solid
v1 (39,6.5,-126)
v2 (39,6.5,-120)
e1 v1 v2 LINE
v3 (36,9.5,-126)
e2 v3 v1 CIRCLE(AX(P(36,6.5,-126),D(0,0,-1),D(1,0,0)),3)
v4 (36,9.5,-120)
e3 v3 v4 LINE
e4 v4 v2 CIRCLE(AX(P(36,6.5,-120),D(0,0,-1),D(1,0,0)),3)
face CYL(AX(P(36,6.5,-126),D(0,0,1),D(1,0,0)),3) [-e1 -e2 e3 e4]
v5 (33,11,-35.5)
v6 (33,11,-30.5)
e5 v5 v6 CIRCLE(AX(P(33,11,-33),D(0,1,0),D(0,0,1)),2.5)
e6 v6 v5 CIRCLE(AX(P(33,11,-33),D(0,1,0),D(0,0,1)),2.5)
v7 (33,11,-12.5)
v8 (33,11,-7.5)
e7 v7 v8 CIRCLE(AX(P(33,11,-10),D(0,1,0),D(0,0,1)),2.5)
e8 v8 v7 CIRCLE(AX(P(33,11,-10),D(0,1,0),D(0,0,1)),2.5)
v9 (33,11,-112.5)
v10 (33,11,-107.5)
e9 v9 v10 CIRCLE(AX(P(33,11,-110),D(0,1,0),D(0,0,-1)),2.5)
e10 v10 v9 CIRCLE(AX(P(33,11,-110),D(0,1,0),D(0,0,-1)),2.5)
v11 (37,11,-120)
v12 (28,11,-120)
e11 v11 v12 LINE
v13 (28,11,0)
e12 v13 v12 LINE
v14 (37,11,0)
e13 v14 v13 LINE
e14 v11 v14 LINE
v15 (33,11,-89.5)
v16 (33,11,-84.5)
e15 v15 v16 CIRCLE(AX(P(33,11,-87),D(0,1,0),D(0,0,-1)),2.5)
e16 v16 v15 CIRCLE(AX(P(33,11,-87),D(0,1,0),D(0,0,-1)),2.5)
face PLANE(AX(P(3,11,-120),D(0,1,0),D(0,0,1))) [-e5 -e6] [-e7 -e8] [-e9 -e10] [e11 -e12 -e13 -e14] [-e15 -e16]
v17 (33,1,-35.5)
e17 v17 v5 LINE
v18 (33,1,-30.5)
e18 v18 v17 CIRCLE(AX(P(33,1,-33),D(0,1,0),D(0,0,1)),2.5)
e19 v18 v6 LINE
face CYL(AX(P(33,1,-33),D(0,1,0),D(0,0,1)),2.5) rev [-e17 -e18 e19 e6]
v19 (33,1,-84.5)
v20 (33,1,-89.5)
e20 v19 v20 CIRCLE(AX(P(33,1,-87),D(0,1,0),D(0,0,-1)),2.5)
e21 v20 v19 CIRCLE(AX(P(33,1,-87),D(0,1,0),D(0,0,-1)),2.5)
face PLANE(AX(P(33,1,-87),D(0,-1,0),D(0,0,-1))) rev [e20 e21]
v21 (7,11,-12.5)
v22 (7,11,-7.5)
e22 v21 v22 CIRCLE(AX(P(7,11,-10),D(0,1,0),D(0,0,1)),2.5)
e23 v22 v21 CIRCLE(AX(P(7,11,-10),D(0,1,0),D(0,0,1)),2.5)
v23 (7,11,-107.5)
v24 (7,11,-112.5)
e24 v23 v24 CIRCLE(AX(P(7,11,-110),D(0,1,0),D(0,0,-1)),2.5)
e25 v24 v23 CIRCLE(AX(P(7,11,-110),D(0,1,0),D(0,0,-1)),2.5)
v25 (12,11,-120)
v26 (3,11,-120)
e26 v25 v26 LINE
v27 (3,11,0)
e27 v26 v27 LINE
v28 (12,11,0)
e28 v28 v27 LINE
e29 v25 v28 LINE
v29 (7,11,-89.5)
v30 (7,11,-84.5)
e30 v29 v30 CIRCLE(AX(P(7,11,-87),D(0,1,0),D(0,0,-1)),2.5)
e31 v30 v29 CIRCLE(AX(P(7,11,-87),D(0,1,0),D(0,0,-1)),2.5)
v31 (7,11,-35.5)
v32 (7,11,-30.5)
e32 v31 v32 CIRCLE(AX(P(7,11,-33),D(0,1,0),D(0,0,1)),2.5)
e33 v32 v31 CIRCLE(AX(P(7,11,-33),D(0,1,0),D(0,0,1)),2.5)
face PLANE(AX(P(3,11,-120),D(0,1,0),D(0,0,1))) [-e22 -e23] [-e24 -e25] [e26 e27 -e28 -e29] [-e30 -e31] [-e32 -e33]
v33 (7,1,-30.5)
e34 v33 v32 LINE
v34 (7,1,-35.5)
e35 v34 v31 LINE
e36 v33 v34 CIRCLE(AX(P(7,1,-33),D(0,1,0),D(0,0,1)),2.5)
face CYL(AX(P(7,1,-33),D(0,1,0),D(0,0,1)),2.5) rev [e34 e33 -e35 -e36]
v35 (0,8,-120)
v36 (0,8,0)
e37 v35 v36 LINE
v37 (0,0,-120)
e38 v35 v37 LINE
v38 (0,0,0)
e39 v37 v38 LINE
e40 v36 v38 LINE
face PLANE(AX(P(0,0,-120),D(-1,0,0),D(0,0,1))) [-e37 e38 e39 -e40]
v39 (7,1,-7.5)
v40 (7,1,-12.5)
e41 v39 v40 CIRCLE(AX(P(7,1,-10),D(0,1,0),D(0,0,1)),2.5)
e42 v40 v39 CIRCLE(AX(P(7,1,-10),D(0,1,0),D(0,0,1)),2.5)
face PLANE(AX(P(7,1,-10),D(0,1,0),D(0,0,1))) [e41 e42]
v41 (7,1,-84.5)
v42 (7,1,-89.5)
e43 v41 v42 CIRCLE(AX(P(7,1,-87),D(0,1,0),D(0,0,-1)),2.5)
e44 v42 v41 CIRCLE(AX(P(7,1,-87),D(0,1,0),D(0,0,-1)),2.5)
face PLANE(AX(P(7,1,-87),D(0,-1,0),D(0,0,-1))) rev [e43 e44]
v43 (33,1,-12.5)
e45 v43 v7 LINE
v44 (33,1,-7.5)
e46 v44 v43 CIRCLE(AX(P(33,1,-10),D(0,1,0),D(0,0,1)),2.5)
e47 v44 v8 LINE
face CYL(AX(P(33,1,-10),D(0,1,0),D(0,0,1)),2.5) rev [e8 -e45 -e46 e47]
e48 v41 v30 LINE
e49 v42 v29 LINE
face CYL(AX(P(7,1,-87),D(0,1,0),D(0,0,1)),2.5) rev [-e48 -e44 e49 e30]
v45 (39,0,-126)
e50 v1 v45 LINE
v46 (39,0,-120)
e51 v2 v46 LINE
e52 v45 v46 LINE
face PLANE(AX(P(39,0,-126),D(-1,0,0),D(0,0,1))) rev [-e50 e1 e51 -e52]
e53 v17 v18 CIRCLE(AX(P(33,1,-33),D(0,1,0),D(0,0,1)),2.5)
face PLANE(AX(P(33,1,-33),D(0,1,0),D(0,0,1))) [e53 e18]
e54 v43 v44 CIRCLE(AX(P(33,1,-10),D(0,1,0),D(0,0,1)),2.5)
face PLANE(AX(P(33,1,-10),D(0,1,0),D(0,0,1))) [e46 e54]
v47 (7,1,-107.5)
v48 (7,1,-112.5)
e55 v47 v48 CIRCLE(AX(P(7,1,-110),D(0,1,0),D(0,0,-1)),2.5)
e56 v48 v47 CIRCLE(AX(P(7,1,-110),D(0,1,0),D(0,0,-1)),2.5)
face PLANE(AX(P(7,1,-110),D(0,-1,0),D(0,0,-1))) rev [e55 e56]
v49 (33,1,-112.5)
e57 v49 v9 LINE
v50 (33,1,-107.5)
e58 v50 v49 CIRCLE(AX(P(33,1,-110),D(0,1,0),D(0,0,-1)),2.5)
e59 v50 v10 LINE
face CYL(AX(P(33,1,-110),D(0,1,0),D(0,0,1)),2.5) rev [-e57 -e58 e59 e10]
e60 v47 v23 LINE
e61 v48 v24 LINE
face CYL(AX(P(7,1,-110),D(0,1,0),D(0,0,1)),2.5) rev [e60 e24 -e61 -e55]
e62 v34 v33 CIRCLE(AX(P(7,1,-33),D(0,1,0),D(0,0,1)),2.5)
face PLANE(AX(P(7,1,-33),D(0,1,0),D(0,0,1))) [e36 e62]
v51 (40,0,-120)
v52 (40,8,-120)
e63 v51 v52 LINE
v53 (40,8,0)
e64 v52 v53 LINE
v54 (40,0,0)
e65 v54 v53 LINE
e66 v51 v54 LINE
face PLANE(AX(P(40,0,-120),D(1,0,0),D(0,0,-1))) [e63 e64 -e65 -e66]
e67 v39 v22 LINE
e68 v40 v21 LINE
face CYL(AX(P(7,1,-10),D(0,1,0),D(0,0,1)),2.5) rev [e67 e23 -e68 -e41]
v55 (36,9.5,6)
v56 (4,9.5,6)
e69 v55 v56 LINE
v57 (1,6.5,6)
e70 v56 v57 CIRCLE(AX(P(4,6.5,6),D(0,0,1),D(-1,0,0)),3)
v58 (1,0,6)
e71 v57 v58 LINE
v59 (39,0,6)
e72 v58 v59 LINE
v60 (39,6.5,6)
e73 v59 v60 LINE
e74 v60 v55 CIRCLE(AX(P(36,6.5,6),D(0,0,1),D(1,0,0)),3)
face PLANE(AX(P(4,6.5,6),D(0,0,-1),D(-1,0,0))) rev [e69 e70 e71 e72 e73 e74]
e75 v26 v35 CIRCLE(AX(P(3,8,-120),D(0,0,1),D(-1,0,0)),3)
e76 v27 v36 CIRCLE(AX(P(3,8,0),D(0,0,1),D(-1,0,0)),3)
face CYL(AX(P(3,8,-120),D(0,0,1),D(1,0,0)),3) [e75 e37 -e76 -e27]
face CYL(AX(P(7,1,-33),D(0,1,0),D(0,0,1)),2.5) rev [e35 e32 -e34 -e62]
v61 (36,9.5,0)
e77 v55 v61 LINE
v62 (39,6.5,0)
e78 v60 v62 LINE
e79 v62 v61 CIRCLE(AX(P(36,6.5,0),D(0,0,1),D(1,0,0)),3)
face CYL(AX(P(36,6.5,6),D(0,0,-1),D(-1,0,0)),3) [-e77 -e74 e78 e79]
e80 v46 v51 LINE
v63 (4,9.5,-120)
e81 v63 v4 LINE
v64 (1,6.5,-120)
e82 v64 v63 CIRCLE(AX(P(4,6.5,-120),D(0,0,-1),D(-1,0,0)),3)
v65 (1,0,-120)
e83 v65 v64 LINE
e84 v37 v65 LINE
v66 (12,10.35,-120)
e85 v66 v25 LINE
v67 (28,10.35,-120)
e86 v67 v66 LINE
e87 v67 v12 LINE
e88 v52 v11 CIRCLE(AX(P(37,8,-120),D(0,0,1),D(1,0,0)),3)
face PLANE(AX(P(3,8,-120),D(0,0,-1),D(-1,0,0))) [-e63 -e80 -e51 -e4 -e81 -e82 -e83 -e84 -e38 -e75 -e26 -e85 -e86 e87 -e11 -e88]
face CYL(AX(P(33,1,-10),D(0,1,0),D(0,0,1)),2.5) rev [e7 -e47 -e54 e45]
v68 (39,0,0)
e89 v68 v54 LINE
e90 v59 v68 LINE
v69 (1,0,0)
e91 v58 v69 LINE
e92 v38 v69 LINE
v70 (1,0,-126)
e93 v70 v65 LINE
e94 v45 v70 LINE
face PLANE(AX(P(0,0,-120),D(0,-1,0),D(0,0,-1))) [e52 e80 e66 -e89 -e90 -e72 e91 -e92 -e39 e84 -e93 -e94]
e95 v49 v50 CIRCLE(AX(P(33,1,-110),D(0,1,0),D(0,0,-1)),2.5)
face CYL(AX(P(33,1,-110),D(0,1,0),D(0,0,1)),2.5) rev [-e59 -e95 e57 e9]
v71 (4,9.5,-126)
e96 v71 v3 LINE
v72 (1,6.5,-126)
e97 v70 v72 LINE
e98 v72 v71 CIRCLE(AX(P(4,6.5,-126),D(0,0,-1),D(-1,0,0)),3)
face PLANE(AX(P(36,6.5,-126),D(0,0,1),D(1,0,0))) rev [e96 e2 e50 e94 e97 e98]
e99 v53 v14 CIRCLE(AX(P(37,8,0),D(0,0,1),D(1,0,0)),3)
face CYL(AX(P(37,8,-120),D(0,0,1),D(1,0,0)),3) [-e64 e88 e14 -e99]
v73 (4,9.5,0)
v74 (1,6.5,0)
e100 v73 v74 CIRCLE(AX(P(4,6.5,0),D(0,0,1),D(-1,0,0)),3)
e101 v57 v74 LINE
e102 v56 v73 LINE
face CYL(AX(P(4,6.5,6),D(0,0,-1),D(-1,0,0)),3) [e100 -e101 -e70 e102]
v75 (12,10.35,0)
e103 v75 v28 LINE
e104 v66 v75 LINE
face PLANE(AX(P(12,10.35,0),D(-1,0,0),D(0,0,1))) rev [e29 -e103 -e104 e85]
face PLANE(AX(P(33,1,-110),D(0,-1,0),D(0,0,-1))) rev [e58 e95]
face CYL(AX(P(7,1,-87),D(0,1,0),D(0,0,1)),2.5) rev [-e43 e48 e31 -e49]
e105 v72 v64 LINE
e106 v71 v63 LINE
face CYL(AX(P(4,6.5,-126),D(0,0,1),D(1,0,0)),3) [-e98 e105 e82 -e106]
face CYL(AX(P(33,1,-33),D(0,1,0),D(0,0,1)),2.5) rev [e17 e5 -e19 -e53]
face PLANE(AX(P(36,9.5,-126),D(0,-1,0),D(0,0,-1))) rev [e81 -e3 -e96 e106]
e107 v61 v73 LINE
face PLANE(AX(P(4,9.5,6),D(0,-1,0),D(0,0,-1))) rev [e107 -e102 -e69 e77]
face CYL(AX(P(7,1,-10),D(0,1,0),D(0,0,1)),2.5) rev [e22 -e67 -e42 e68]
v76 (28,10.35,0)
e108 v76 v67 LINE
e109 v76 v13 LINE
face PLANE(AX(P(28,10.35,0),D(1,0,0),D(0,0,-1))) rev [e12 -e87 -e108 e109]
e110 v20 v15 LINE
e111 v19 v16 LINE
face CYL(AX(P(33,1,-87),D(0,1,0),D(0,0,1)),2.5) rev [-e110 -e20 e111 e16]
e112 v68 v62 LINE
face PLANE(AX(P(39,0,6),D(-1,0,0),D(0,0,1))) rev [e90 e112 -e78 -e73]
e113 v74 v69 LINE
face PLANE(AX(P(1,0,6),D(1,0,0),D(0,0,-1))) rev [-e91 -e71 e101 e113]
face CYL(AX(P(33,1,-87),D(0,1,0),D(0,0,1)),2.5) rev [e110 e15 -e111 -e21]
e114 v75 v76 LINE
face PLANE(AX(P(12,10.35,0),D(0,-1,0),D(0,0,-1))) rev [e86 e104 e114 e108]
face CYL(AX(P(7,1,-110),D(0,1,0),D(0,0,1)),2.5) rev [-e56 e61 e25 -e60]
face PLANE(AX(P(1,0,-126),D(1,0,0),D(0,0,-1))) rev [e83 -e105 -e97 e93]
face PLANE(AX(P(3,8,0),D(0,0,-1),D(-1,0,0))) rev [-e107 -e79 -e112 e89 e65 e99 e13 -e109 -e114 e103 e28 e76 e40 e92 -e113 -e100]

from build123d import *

# Parameters (mm, degrees)
EXTRUDE_263_DEPTH   = 120
EXTRUDE_1_DEPTH     = 6
EXTRUDE_START       = 6
EXTRUDE_2_DEPTH     = 6
SKETCH_4_R          = 2.5
CUT_EXTRUDE_1_DEPTH = 10
SKETCH_5_W          = 16
SKETCH_5_H          = 120
CUT_EXTRUDE_2_DEPTH = 0.65


with BuildPart() as part:
    # 草图1 → Extrude 263 (new body)
    with BuildSketch(Plane.XY):
        with BuildLine():
            Line((0, 0), (40, 0))
            Line((40, 0), (40, 8))
            ThreePointArc((40, 8), (39.121320344, 10.121320344), (37, 11))
            Line((37, 11), (3, 11))
            ThreePointArc((3, 11), (0.878679656, 10.121320344), (0, 8))
            Line((0, 8), (0, 0))
        make_face()
    extrude(amount=-EXTRUDE_263_DEPTH)

    # 草图2 → 凸台-拉伸1 (add)
    with BuildSketch(Plane.XY):
        with BuildLine():
            Line((1, 0), (39, 0))
            Line((39, 0), (39, 6.5))
            ThreePointArc((39, 6.5), (38.121320344, 8.621320344), (36, 9.5))
            Line((36, 9.5), (4, 9.5))
            ThreePointArc((4, 9.5), (1.878679656, 8.621320344), (1, 6.5))
            Line((1, 6.5), (1, 0))
        make_face()
    extrude(amount=EXTRUDE_1_DEPTH)

    # 草图3 → 凸台-拉伸2 (add)
    with BuildSketch(Plane(origin=(0, 0, -120), x_dir=(-1, 0, 0), z_dir=(0, 0, -1)).offset(EXTRUDE_START)):
        with BuildLine():
            Line((-39, 0), (-1, 0))
            Line((-1, 0), (-1, 6.5))
            ThreePointArc((-1, 6.5), (-1.878679656, 8.621320344), (-4, 9.5))
            Line((-4, 9.5), (-36, 9.5))
            ThreePointArc((-36, 9.5), (-38.121320344, 8.621320344), (-39, 6.5))
            Line((-39, 6.5), (-39, 0))
        make_face()
    extrude(amount=-EXTRUDE_2_DEPTH)

    # 草图4 → 切除-拉伸1 (cut)
    with BuildSketch(Plane(origin=(0, 11, 0), x_dir=(-1, 0, 0), z_dir=(0, 1, 0))):
        with Locations(Location((-33, -10, 0), (0, 0, 90))):
            Circle(SKETCH_4_R)
        with Locations(Location((-7, -10, 0), (0, 0, 90))):
            Circle(SKETCH_4_R)
        with Locations(Location((-33, -33, 0), (0, 0, 90))):
            Circle(SKETCH_4_R)
        with Locations(Location((-7, -33, 0), (0, 0, 90))):
            Circle(SKETCH_4_R)
        with Locations(Location((-7, -87, 0), (0, 0, 270))):
            Circle(SKETCH_4_R)
        with Locations(Location((-33, -87, 0), (0, 0, 270))):
            Circle(SKETCH_4_R)
        with Locations(Location((-7, -110, 0), (0, 0, 270))):
            Circle(SKETCH_4_R)
        with Locations(Location((-33, -110, 0), (0, 0, 270))):
            Circle(SKETCH_4_R)
    extrude(amount=-CUT_EXTRUDE_1_DEPTH, mode=Mode.SUBTRACT)

    # 草图5 → 切除-拉伸2 (cut)
    with BuildSketch(Plane(origin=(0, 11, 0), x_dir=(-1, 0, 0), z_dir=(0, 1, 0))):
        with Locations((-20, -60)):
            Rectangle(SKETCH_5_W, SKETCH_5_H)
    extrude(amount=-CUT_EXTRUDE_2_DEPTH, mode=Mode.SUBTRACT)


solid = part.part
